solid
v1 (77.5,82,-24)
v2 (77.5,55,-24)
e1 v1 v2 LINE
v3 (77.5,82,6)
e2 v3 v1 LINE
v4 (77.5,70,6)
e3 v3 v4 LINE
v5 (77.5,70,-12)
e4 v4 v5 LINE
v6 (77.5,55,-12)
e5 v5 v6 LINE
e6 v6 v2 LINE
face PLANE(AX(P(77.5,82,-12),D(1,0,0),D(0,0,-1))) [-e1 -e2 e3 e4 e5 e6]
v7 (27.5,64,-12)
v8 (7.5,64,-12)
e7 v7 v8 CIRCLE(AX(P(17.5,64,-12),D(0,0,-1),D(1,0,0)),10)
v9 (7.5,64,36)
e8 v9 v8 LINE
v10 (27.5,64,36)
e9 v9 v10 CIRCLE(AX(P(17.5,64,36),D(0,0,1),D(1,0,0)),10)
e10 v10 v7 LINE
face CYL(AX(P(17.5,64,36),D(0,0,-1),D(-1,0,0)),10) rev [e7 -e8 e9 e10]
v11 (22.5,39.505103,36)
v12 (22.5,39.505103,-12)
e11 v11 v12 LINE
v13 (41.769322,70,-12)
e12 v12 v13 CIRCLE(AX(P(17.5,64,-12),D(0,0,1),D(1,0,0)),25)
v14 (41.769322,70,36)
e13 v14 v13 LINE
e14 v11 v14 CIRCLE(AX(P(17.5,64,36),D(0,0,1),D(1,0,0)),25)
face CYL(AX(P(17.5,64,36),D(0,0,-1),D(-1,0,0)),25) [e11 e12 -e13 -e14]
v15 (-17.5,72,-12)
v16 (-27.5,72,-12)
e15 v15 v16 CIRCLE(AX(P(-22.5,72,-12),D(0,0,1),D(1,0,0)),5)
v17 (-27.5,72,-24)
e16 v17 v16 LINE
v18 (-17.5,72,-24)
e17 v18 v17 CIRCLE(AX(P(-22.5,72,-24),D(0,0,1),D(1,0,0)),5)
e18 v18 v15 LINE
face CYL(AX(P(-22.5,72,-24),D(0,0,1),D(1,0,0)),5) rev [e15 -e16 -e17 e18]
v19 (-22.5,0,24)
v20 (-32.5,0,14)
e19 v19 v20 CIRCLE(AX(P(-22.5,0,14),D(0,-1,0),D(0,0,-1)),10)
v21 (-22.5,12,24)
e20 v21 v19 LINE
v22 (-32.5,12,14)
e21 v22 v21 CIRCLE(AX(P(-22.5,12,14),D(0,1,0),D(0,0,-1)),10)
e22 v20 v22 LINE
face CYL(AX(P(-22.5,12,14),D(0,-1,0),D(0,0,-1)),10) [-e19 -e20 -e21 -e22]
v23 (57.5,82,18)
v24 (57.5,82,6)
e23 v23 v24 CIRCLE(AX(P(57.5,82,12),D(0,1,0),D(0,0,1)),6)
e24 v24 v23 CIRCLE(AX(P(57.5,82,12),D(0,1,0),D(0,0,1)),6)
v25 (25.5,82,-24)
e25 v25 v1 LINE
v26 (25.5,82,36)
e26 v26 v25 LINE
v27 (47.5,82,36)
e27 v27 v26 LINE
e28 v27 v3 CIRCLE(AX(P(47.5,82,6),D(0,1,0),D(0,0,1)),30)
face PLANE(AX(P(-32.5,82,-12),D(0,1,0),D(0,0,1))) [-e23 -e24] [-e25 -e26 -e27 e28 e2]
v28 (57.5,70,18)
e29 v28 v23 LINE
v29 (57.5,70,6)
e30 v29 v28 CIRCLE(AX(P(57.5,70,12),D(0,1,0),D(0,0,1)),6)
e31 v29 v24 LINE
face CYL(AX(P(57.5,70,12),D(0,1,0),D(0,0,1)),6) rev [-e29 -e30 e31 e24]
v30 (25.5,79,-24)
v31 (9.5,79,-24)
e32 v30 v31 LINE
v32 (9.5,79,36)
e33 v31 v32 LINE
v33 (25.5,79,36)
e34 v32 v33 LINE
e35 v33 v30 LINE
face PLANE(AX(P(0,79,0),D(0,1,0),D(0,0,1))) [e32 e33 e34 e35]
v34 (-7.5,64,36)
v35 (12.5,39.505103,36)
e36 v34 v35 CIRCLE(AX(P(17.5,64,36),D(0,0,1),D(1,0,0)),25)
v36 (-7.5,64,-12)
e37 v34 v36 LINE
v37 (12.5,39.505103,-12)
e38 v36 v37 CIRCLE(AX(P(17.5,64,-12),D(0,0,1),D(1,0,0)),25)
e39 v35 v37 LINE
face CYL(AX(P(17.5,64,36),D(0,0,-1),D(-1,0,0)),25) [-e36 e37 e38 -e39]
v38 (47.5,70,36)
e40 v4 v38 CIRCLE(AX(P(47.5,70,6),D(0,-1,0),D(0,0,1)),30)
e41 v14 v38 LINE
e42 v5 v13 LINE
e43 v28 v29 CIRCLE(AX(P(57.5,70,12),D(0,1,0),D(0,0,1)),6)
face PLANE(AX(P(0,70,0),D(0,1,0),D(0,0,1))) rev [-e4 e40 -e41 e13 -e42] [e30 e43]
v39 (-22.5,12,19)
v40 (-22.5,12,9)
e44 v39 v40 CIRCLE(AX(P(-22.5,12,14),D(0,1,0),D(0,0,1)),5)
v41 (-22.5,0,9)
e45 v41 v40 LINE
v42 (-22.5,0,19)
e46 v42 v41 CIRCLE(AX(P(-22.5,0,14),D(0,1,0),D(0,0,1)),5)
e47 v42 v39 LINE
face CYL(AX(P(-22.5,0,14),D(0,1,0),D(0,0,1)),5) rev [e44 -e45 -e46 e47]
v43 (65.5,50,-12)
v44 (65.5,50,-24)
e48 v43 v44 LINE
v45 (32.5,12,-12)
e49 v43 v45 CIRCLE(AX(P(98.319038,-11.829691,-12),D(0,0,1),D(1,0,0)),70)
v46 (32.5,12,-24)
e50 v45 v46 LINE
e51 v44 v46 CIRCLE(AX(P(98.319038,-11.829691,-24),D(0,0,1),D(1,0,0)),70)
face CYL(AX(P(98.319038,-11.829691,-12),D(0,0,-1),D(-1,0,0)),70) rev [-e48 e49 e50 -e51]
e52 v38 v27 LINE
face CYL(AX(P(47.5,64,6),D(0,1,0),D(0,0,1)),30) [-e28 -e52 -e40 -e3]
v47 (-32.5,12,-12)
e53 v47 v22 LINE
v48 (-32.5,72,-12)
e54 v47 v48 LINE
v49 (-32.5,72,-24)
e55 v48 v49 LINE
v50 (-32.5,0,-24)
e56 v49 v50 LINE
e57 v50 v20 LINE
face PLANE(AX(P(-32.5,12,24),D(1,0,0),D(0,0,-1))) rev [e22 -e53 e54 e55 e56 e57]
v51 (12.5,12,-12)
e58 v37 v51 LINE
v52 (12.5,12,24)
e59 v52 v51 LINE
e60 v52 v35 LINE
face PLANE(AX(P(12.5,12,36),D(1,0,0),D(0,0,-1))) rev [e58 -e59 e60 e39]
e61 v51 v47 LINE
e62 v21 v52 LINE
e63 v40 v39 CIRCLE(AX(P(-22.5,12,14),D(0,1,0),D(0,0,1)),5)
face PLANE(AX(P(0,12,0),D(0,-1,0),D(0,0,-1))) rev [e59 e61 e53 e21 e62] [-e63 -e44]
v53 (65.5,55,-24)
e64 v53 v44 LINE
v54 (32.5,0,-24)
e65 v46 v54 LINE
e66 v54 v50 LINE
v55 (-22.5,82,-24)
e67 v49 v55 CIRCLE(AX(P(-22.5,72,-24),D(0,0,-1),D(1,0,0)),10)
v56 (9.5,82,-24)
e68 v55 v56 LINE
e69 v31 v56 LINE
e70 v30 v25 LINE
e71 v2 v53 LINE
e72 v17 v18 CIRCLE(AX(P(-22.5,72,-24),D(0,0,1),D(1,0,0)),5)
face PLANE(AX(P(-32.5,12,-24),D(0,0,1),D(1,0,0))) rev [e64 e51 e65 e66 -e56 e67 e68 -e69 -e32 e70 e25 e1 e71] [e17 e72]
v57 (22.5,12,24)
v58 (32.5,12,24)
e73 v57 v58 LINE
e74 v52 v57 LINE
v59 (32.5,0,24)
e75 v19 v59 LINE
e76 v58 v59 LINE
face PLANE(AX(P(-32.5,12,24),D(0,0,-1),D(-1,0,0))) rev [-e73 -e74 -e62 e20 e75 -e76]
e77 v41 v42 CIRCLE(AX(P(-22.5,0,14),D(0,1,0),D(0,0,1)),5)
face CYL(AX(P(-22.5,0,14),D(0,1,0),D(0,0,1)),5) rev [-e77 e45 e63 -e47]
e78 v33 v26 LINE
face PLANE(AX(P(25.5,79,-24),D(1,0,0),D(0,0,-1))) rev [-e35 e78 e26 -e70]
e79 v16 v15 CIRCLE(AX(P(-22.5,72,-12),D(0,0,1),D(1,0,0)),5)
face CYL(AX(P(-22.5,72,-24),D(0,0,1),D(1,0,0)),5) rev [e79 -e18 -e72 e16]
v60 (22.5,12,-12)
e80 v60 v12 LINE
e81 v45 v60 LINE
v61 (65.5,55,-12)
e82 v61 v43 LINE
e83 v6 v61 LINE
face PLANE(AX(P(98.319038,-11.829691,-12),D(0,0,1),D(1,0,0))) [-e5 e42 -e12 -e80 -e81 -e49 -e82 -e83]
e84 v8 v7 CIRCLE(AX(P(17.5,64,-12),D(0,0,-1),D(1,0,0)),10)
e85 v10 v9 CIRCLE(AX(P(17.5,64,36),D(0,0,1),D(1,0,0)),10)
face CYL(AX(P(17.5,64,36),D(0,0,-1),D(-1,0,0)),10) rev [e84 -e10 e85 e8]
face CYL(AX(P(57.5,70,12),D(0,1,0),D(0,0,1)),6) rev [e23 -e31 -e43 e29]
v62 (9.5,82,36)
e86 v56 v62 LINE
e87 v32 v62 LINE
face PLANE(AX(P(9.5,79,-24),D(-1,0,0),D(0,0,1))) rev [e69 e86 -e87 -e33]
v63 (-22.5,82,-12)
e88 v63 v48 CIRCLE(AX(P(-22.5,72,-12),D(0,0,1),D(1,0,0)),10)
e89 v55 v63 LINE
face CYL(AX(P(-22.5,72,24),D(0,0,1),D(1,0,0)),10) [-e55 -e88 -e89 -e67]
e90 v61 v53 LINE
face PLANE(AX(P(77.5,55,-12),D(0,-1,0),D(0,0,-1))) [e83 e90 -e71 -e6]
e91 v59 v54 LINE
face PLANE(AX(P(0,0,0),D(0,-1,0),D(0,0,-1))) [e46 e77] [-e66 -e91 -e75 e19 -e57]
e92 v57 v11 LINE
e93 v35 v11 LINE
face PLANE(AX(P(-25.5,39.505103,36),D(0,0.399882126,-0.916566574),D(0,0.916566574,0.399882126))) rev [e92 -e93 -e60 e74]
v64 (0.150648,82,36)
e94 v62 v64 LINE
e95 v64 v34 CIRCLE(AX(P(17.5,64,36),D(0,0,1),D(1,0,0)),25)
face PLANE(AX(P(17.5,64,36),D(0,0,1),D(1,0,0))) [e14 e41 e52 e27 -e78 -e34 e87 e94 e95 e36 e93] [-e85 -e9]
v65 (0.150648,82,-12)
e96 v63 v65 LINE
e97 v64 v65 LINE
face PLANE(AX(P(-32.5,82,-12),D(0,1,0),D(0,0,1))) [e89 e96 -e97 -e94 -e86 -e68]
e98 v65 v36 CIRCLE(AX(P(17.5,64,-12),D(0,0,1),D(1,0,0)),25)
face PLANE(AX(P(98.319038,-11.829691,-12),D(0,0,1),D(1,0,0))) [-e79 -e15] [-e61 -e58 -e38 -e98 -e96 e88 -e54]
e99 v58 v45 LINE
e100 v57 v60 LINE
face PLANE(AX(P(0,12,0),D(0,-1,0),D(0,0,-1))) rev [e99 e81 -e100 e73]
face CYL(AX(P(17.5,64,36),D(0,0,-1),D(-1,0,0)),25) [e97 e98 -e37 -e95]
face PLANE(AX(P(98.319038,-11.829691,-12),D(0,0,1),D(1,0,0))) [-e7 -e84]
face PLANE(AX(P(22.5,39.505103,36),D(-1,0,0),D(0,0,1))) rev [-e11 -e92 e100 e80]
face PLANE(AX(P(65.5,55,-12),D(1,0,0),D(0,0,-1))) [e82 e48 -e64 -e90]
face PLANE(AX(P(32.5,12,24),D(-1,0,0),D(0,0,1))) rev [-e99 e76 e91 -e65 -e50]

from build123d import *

# Parameters (mm, degrees)
BASE_PLATE_SKETCH_W          = 65
BASE_PLATE_SKETCH_H          = 48
BASE_PLATE_DEPTH             = 12
UPPER_BLOCK_DEPTH            = 12
SUPPORT_WEB_SKETCH_R         = 10
SUPPORT_WEB_DEPTH            = 48
TOP_SLOT_SKETCH_W            = 16
TOP_SLOT_SKETCH_H            = 60
TOP_SLOT_DEPTH               = 3
HUB_BOSS_SKETCH_W            = 52
HUB_BOSS_SKETCH_H            = 60
HUB_BOSS_SKETCH_R            = 6
HUB_BOSS_DEPTH               = 12
HUB_ROUND_R30_R              = 30
UPPER_MOUNTING_HOLE_SKETCH_R = 5
UPPER_MOUNTING_HOLE_DEPTH    = 12
BASE_MOUNTING_HOLE_SKETCH_R  = 5
BASE_MOUNTING_HOLE_DEPTH     = 12
UPPER_BLOCK_FILLET_R10_R     = 10
SIDE_SUPPORT_DEPTH           = 48
SIDE_RELIEF_CUT_DEPTH        = 48


with BuildPart() as part:
    # Base Plate Sketch → Base Plate (new body)
    with BuildSketch(Plane(origin=(0, 0, 0), x_dir=(1, 0, 0), z_dir=(0, 1, 0))):
        Rectangle(BASE_PLATE_SKETCH_W, BASE_PLATE_SKETCH_H)
    extrude(amount=BASE_PLATE_DEPTH)

    # Upper Block Sketch → Upper Block (add)
    with BuildSketch(Plane(origin=(0, 0, -24), x_dir=(-1, 0, 0), z_dir=(0, 0, -1))):
        with BuildLine():
            Line((32.5, 12), (32.5, 82))
            Line((32.5, 82), (-77.5, 82))
            Line((-77.5, 82), (-77.5, 55))
            Line((-77.5, 55), (-65.5, 55))
            Line((-65.5, 55), (-65.5, 50))
            ThreePointArc((-65.5, 50), (-45.466720109, 34.068374642), (-32.5, 12))
            Line((-32.5, 12), (32.5, 12))
        make_face()
    extrude(amount=-UPPER_BLOCK_DEPTH)

    # Support Web Sketch → Support Web (add)
    with BuildSketch(Plane.XY.offset(-12)):
        with BuildLine():
            Line((0.150648427, 82), (34.849351573, 82))
            ThreePointArc((34.849351573, 82), (17.5, 39), (0.150648427, 82))
        make_face()
        with Locations((17.5, 64)):
            Circle(SUPPORT_WEB_SKETCH_R, mode=Mode.SUBTRACT)
    extrude(amount=SUPPORT_WEB_DEPTH)

    # Top Slot Sketch → Top Slot (cut)
    with BuildSketch(Plane(origin=(0, 82, 0), x_dir=(1, 0, 0), z_dir=(0, 1, 0))):
        with Locations((17.5, -6)):
            Rectangle(TOP_SLOT_SKETCH_W, TOP_SLOT_SKETCH_H)
    extrude(amount=-TOP_SLOT_DEPTH, mode=Mode.SUBTRACT)

    # Hub Boss Sketch → Hub Boss (add)
    with BuildSketch(Plane(origin=(0, 82, 0), x_dir=(1, 0, 0), z_dir=(0, 1, 0))):
        with Locations((51.5, -6)):
            Rectangle(HUB_BOSS_SKETCH_W, HUB_BOSS_SKETCH_H)
        with Locations(Location((57.5, -12, 0), (0, 0, 270))):
            Circle(HUB_BOSS_SKETCH_R, mode=Mode.SUBTRACT)
    extrude(amount=-HUB_BOSS_DEPTH)

    # Hub Round R30
    hub_round_r30_edges = [part.edges().sort_by_distance(p)[0] for p in [
        (77.5, 76, 36),
    ]]
    fillet(hub_round_r30_edges, radius=HUB_ROUND_R30_R)

    # Upper Mounting Hole Sketch → Upper Mounting Hole (cut)
    with BuildSketch(Plane.XY.offset(-12)):
        with Locations((-22.5, 72)):
            Circle(UPPER_MOUNTING_HOLE_SKETCH_R)
    extrude(amount=-UPPER_MOUNTING_HOLE_DEPTH, mode=Mode.SUBTRACT)

    # Base Mounting Hole Sketch → Base Mounting Hole (cut)
    with BuildSketch(Plane(origin=(0, 12, 0), x_dir=(1, 0, 0), z_dir=(0, 1, 0))):
        with Locations(Location((-22.5, -14, 0), (0, 0, 270))):
            Circle(BASE_MOUNTING_HOLE_SKETCH_R)
    extrude(amount=-BASE_MOUNTING_HOLE_DEPTH, mode=Mode.SUBTRACT)

    # Upper Block Fillet R10
    upper_block_fillet_r10_edges = [part.edges().sort_by_distance(p)[0] for p in [
        (-32.5, 82, -18),
        (-32.5, 6, 24),
    ]]
    fillet(upper_block_fillet_r10_edges, radius=UPPER_BLOCK_FILLET_R10_R)

    # Side Support Sketch → Side Support (add)
    with BuildSketch(Plane.XY.offset(-12)):
        with BuildLine():
            Line((17.5, 12), (12.5, 12))
            Line((12.5, 12), (12.5, 39.505102572))
            ThreePointArc((12.5, 39.505102572), (17.5, 39), (22.5, 39.505102572))
            Line((22.5, 39.505102572), (22.5, 12))
            Line((22.5, 12), (17.5, 12))
        make_face()
    extrude(amount=SIDE_SUPPORT_DEPTH)

    # Side Relief Sketch → Side Relief Cut (cut)
    with BuildSketch(Plane(origin=(22.5, 0, 0), x_dir=(0, 0, -1), z_dir=(1, 0, 0))):
        Polygon((-36, 39.505102572), (-24, 12), (-36, 12), align=None)
    extrude(amount=-SIDE_RELIEF_CUT_DEPTH, mode=Mode.SUBTRACT)


solid = part.part
